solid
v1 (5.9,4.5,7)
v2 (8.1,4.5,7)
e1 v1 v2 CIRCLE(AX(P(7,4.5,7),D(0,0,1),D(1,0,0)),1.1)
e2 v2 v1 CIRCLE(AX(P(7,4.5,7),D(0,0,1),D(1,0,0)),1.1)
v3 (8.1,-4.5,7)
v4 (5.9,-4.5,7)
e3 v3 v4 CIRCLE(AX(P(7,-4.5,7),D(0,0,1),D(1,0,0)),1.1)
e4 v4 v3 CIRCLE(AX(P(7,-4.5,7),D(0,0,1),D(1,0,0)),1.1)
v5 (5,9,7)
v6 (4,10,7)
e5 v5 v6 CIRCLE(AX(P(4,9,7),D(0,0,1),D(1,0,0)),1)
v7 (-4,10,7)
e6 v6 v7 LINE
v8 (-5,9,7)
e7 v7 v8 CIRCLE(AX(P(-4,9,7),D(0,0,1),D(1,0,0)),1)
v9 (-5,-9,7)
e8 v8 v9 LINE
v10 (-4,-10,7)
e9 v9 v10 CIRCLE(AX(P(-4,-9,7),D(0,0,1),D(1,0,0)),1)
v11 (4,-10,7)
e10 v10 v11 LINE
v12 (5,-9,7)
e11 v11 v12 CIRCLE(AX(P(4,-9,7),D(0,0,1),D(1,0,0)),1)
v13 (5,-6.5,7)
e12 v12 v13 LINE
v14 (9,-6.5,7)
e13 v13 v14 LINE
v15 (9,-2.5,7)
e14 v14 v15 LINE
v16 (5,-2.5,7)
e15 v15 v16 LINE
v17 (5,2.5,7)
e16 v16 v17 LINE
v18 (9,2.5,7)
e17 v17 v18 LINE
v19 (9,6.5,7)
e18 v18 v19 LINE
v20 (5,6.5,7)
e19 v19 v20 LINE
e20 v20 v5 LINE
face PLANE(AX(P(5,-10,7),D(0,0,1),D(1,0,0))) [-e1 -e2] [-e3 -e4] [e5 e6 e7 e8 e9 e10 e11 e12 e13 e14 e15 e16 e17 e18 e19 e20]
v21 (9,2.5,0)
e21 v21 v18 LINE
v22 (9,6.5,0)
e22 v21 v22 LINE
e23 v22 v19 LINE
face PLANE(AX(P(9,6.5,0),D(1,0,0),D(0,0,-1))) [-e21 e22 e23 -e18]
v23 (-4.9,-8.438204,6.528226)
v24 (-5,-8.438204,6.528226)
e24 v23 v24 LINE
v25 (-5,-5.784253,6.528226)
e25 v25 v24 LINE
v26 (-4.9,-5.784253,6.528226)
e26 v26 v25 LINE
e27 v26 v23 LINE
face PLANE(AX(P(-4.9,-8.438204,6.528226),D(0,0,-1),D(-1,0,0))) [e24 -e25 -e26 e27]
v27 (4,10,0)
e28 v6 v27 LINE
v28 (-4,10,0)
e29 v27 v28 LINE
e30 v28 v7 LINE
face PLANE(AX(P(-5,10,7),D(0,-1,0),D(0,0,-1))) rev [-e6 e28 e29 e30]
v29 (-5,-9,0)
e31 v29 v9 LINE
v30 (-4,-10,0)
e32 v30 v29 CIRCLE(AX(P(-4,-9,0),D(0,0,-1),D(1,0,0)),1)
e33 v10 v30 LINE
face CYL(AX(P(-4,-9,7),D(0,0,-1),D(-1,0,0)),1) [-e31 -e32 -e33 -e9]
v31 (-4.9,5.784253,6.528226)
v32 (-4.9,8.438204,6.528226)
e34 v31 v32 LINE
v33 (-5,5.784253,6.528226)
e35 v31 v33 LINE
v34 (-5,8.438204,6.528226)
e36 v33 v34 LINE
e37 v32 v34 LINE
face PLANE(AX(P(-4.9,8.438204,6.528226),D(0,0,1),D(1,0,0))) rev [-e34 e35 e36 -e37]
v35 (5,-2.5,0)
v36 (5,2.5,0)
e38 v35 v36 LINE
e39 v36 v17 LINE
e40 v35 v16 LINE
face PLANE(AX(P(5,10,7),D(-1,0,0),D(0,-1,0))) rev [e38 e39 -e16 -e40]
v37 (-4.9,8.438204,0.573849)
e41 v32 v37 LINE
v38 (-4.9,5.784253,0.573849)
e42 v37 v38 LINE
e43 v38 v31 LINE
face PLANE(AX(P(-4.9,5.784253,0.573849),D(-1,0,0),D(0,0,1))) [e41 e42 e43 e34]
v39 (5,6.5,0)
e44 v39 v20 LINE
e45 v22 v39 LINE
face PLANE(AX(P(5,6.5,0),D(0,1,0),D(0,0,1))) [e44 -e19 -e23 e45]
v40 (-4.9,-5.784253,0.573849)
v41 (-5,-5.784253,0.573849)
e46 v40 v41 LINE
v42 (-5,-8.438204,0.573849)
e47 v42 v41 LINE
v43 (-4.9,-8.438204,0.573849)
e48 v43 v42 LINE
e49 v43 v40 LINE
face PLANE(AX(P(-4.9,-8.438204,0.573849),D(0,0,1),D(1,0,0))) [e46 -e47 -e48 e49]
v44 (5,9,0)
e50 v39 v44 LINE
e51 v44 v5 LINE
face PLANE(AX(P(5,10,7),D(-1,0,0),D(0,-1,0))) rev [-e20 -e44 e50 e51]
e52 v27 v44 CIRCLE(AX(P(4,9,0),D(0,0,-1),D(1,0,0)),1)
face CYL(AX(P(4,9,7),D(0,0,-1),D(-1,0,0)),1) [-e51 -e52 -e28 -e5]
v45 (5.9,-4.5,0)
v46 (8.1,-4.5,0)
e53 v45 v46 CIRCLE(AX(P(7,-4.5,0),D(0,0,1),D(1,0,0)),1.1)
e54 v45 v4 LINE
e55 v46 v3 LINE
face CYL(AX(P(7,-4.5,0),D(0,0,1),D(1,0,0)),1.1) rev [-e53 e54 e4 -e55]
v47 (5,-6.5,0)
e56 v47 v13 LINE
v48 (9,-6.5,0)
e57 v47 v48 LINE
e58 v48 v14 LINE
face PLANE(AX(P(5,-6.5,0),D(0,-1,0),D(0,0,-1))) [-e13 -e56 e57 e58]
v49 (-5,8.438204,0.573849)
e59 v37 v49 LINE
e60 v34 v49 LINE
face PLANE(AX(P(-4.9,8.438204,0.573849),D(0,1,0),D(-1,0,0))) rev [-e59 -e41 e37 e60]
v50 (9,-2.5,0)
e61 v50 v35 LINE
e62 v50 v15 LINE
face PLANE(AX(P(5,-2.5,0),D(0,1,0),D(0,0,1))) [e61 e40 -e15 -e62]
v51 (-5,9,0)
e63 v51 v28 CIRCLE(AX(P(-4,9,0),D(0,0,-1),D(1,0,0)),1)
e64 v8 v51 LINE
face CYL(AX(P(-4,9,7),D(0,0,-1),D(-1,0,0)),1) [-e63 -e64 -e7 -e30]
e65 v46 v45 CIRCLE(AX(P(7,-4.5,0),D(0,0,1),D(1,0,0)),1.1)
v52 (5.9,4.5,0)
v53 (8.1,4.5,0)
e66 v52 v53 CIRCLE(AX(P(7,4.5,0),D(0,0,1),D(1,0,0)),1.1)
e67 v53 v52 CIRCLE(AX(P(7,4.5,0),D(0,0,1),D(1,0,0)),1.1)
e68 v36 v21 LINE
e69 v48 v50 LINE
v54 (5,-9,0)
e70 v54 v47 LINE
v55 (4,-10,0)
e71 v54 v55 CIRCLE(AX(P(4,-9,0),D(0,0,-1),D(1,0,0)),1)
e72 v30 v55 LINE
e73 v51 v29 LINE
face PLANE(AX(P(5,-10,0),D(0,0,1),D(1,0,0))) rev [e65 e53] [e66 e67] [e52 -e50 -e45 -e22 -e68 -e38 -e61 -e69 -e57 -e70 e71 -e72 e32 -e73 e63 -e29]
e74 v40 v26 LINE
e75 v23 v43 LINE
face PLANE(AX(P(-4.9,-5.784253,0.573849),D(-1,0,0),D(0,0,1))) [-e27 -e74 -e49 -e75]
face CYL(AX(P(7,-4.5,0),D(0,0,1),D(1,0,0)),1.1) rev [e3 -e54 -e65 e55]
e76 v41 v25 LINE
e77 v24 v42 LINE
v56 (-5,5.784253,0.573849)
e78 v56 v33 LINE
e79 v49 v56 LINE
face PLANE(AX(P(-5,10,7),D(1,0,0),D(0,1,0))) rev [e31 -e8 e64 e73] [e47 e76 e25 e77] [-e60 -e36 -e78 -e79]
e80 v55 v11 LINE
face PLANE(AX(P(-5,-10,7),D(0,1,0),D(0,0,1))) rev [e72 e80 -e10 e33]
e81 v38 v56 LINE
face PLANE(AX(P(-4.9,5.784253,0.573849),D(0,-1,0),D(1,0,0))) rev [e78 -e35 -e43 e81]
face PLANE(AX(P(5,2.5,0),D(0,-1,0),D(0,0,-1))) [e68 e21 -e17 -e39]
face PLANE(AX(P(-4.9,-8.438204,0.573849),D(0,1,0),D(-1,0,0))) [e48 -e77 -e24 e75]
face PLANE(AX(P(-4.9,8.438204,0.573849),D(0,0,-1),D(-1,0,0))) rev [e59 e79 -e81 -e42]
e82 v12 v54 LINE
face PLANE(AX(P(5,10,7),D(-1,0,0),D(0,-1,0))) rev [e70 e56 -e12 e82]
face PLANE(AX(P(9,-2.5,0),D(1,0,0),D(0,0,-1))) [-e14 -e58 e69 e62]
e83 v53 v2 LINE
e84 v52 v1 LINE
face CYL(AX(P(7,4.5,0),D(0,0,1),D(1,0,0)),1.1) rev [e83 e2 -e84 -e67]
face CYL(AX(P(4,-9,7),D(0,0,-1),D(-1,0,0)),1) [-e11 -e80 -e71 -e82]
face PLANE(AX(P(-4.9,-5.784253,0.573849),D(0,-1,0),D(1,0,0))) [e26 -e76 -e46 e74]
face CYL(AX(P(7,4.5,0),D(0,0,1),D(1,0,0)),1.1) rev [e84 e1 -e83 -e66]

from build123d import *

# Parameters (mm, degrees)
SKETCH_1_W          = 10
SKETCH_1_H          = 20
EXTRUDE_1_DEPTH     = 7
SKETCH_2_W          = 4
SKETCH_2_H          = 4
SKETCH_2_R          = 1.1
EXTRUDE_2_DEPTH     = 7
FILLET_1_R          = 1
SKETCH_3_W          = 5.954377652
SKETCH_3_H          = 2.653951182
CUT_EXTRUDE_1_DEPTH = 0.1


with BuildPart() as part:
    # 草图1 → 凸台-拉伸1 (new body)
    with BuildSketch(Plane.XY):
        Rectangle(SKETCH_1_W, SKETCH_1_H)
    extrude(amount=EXTRUDE_1_DEPTH)

    # 草图2 → 凸台-拉伸2 (add)
    # profile 1 of 2: a face of its own
    with BuildSketch(Plane.XY.offset(7)):
        with Locations((7, 4.5)):
            Rectangle(SKETCH_2_W, SKETCH_2_H)
        with Locations((7, 4.5)):
            Circle(SKETCH_2_R, mode=Mode.SUBTRACT)
    # profile 2 of 2: a face of its own
    with BuildSketch(Plane.XY.offset(7)):
        with Locations((7, -4.5)):
            Rectangle(SKETCH_2_W, SKETCH_2_H)
        with Locations((7, -4.5)):
            Circle(SKETCH_2_R, mode=Mode.SUBTRACT)
    extrude(amount=-EXTRUDE_2_DEPTH)

    # 圆角1
    fillet_1_edges = [part.edges().sort_by_distance(p)[0] for p in [
        (5, -10, 3.5),
        (-5, -10, 3.5),
        (5, 10, 3.5),
        (-5, 10, 3.5),
    ]]
    fillet(fillet_1_edges, radius=FILLET_1_R)

    # 草图3 → 切除-拉伸1 (cut)
    with BuildSketch(Plane.ZY.offset(5)):
        with Locations((3.551037523, 7.111228168)):
            Rectangle(SKETCH_3_W, SKETCH_3_H)
    cut_extrude_1 = extrude(amount=-CUT_EXTRUDE_1_DEPTH, mode=Mode.SUBTRACT)

    # 镜向1: 切除-拉伸1 across plane
    add(cut_extrude_1.mirror(Plane.ZX), mode=Mode.SUBTRACT)


solid = part.part
